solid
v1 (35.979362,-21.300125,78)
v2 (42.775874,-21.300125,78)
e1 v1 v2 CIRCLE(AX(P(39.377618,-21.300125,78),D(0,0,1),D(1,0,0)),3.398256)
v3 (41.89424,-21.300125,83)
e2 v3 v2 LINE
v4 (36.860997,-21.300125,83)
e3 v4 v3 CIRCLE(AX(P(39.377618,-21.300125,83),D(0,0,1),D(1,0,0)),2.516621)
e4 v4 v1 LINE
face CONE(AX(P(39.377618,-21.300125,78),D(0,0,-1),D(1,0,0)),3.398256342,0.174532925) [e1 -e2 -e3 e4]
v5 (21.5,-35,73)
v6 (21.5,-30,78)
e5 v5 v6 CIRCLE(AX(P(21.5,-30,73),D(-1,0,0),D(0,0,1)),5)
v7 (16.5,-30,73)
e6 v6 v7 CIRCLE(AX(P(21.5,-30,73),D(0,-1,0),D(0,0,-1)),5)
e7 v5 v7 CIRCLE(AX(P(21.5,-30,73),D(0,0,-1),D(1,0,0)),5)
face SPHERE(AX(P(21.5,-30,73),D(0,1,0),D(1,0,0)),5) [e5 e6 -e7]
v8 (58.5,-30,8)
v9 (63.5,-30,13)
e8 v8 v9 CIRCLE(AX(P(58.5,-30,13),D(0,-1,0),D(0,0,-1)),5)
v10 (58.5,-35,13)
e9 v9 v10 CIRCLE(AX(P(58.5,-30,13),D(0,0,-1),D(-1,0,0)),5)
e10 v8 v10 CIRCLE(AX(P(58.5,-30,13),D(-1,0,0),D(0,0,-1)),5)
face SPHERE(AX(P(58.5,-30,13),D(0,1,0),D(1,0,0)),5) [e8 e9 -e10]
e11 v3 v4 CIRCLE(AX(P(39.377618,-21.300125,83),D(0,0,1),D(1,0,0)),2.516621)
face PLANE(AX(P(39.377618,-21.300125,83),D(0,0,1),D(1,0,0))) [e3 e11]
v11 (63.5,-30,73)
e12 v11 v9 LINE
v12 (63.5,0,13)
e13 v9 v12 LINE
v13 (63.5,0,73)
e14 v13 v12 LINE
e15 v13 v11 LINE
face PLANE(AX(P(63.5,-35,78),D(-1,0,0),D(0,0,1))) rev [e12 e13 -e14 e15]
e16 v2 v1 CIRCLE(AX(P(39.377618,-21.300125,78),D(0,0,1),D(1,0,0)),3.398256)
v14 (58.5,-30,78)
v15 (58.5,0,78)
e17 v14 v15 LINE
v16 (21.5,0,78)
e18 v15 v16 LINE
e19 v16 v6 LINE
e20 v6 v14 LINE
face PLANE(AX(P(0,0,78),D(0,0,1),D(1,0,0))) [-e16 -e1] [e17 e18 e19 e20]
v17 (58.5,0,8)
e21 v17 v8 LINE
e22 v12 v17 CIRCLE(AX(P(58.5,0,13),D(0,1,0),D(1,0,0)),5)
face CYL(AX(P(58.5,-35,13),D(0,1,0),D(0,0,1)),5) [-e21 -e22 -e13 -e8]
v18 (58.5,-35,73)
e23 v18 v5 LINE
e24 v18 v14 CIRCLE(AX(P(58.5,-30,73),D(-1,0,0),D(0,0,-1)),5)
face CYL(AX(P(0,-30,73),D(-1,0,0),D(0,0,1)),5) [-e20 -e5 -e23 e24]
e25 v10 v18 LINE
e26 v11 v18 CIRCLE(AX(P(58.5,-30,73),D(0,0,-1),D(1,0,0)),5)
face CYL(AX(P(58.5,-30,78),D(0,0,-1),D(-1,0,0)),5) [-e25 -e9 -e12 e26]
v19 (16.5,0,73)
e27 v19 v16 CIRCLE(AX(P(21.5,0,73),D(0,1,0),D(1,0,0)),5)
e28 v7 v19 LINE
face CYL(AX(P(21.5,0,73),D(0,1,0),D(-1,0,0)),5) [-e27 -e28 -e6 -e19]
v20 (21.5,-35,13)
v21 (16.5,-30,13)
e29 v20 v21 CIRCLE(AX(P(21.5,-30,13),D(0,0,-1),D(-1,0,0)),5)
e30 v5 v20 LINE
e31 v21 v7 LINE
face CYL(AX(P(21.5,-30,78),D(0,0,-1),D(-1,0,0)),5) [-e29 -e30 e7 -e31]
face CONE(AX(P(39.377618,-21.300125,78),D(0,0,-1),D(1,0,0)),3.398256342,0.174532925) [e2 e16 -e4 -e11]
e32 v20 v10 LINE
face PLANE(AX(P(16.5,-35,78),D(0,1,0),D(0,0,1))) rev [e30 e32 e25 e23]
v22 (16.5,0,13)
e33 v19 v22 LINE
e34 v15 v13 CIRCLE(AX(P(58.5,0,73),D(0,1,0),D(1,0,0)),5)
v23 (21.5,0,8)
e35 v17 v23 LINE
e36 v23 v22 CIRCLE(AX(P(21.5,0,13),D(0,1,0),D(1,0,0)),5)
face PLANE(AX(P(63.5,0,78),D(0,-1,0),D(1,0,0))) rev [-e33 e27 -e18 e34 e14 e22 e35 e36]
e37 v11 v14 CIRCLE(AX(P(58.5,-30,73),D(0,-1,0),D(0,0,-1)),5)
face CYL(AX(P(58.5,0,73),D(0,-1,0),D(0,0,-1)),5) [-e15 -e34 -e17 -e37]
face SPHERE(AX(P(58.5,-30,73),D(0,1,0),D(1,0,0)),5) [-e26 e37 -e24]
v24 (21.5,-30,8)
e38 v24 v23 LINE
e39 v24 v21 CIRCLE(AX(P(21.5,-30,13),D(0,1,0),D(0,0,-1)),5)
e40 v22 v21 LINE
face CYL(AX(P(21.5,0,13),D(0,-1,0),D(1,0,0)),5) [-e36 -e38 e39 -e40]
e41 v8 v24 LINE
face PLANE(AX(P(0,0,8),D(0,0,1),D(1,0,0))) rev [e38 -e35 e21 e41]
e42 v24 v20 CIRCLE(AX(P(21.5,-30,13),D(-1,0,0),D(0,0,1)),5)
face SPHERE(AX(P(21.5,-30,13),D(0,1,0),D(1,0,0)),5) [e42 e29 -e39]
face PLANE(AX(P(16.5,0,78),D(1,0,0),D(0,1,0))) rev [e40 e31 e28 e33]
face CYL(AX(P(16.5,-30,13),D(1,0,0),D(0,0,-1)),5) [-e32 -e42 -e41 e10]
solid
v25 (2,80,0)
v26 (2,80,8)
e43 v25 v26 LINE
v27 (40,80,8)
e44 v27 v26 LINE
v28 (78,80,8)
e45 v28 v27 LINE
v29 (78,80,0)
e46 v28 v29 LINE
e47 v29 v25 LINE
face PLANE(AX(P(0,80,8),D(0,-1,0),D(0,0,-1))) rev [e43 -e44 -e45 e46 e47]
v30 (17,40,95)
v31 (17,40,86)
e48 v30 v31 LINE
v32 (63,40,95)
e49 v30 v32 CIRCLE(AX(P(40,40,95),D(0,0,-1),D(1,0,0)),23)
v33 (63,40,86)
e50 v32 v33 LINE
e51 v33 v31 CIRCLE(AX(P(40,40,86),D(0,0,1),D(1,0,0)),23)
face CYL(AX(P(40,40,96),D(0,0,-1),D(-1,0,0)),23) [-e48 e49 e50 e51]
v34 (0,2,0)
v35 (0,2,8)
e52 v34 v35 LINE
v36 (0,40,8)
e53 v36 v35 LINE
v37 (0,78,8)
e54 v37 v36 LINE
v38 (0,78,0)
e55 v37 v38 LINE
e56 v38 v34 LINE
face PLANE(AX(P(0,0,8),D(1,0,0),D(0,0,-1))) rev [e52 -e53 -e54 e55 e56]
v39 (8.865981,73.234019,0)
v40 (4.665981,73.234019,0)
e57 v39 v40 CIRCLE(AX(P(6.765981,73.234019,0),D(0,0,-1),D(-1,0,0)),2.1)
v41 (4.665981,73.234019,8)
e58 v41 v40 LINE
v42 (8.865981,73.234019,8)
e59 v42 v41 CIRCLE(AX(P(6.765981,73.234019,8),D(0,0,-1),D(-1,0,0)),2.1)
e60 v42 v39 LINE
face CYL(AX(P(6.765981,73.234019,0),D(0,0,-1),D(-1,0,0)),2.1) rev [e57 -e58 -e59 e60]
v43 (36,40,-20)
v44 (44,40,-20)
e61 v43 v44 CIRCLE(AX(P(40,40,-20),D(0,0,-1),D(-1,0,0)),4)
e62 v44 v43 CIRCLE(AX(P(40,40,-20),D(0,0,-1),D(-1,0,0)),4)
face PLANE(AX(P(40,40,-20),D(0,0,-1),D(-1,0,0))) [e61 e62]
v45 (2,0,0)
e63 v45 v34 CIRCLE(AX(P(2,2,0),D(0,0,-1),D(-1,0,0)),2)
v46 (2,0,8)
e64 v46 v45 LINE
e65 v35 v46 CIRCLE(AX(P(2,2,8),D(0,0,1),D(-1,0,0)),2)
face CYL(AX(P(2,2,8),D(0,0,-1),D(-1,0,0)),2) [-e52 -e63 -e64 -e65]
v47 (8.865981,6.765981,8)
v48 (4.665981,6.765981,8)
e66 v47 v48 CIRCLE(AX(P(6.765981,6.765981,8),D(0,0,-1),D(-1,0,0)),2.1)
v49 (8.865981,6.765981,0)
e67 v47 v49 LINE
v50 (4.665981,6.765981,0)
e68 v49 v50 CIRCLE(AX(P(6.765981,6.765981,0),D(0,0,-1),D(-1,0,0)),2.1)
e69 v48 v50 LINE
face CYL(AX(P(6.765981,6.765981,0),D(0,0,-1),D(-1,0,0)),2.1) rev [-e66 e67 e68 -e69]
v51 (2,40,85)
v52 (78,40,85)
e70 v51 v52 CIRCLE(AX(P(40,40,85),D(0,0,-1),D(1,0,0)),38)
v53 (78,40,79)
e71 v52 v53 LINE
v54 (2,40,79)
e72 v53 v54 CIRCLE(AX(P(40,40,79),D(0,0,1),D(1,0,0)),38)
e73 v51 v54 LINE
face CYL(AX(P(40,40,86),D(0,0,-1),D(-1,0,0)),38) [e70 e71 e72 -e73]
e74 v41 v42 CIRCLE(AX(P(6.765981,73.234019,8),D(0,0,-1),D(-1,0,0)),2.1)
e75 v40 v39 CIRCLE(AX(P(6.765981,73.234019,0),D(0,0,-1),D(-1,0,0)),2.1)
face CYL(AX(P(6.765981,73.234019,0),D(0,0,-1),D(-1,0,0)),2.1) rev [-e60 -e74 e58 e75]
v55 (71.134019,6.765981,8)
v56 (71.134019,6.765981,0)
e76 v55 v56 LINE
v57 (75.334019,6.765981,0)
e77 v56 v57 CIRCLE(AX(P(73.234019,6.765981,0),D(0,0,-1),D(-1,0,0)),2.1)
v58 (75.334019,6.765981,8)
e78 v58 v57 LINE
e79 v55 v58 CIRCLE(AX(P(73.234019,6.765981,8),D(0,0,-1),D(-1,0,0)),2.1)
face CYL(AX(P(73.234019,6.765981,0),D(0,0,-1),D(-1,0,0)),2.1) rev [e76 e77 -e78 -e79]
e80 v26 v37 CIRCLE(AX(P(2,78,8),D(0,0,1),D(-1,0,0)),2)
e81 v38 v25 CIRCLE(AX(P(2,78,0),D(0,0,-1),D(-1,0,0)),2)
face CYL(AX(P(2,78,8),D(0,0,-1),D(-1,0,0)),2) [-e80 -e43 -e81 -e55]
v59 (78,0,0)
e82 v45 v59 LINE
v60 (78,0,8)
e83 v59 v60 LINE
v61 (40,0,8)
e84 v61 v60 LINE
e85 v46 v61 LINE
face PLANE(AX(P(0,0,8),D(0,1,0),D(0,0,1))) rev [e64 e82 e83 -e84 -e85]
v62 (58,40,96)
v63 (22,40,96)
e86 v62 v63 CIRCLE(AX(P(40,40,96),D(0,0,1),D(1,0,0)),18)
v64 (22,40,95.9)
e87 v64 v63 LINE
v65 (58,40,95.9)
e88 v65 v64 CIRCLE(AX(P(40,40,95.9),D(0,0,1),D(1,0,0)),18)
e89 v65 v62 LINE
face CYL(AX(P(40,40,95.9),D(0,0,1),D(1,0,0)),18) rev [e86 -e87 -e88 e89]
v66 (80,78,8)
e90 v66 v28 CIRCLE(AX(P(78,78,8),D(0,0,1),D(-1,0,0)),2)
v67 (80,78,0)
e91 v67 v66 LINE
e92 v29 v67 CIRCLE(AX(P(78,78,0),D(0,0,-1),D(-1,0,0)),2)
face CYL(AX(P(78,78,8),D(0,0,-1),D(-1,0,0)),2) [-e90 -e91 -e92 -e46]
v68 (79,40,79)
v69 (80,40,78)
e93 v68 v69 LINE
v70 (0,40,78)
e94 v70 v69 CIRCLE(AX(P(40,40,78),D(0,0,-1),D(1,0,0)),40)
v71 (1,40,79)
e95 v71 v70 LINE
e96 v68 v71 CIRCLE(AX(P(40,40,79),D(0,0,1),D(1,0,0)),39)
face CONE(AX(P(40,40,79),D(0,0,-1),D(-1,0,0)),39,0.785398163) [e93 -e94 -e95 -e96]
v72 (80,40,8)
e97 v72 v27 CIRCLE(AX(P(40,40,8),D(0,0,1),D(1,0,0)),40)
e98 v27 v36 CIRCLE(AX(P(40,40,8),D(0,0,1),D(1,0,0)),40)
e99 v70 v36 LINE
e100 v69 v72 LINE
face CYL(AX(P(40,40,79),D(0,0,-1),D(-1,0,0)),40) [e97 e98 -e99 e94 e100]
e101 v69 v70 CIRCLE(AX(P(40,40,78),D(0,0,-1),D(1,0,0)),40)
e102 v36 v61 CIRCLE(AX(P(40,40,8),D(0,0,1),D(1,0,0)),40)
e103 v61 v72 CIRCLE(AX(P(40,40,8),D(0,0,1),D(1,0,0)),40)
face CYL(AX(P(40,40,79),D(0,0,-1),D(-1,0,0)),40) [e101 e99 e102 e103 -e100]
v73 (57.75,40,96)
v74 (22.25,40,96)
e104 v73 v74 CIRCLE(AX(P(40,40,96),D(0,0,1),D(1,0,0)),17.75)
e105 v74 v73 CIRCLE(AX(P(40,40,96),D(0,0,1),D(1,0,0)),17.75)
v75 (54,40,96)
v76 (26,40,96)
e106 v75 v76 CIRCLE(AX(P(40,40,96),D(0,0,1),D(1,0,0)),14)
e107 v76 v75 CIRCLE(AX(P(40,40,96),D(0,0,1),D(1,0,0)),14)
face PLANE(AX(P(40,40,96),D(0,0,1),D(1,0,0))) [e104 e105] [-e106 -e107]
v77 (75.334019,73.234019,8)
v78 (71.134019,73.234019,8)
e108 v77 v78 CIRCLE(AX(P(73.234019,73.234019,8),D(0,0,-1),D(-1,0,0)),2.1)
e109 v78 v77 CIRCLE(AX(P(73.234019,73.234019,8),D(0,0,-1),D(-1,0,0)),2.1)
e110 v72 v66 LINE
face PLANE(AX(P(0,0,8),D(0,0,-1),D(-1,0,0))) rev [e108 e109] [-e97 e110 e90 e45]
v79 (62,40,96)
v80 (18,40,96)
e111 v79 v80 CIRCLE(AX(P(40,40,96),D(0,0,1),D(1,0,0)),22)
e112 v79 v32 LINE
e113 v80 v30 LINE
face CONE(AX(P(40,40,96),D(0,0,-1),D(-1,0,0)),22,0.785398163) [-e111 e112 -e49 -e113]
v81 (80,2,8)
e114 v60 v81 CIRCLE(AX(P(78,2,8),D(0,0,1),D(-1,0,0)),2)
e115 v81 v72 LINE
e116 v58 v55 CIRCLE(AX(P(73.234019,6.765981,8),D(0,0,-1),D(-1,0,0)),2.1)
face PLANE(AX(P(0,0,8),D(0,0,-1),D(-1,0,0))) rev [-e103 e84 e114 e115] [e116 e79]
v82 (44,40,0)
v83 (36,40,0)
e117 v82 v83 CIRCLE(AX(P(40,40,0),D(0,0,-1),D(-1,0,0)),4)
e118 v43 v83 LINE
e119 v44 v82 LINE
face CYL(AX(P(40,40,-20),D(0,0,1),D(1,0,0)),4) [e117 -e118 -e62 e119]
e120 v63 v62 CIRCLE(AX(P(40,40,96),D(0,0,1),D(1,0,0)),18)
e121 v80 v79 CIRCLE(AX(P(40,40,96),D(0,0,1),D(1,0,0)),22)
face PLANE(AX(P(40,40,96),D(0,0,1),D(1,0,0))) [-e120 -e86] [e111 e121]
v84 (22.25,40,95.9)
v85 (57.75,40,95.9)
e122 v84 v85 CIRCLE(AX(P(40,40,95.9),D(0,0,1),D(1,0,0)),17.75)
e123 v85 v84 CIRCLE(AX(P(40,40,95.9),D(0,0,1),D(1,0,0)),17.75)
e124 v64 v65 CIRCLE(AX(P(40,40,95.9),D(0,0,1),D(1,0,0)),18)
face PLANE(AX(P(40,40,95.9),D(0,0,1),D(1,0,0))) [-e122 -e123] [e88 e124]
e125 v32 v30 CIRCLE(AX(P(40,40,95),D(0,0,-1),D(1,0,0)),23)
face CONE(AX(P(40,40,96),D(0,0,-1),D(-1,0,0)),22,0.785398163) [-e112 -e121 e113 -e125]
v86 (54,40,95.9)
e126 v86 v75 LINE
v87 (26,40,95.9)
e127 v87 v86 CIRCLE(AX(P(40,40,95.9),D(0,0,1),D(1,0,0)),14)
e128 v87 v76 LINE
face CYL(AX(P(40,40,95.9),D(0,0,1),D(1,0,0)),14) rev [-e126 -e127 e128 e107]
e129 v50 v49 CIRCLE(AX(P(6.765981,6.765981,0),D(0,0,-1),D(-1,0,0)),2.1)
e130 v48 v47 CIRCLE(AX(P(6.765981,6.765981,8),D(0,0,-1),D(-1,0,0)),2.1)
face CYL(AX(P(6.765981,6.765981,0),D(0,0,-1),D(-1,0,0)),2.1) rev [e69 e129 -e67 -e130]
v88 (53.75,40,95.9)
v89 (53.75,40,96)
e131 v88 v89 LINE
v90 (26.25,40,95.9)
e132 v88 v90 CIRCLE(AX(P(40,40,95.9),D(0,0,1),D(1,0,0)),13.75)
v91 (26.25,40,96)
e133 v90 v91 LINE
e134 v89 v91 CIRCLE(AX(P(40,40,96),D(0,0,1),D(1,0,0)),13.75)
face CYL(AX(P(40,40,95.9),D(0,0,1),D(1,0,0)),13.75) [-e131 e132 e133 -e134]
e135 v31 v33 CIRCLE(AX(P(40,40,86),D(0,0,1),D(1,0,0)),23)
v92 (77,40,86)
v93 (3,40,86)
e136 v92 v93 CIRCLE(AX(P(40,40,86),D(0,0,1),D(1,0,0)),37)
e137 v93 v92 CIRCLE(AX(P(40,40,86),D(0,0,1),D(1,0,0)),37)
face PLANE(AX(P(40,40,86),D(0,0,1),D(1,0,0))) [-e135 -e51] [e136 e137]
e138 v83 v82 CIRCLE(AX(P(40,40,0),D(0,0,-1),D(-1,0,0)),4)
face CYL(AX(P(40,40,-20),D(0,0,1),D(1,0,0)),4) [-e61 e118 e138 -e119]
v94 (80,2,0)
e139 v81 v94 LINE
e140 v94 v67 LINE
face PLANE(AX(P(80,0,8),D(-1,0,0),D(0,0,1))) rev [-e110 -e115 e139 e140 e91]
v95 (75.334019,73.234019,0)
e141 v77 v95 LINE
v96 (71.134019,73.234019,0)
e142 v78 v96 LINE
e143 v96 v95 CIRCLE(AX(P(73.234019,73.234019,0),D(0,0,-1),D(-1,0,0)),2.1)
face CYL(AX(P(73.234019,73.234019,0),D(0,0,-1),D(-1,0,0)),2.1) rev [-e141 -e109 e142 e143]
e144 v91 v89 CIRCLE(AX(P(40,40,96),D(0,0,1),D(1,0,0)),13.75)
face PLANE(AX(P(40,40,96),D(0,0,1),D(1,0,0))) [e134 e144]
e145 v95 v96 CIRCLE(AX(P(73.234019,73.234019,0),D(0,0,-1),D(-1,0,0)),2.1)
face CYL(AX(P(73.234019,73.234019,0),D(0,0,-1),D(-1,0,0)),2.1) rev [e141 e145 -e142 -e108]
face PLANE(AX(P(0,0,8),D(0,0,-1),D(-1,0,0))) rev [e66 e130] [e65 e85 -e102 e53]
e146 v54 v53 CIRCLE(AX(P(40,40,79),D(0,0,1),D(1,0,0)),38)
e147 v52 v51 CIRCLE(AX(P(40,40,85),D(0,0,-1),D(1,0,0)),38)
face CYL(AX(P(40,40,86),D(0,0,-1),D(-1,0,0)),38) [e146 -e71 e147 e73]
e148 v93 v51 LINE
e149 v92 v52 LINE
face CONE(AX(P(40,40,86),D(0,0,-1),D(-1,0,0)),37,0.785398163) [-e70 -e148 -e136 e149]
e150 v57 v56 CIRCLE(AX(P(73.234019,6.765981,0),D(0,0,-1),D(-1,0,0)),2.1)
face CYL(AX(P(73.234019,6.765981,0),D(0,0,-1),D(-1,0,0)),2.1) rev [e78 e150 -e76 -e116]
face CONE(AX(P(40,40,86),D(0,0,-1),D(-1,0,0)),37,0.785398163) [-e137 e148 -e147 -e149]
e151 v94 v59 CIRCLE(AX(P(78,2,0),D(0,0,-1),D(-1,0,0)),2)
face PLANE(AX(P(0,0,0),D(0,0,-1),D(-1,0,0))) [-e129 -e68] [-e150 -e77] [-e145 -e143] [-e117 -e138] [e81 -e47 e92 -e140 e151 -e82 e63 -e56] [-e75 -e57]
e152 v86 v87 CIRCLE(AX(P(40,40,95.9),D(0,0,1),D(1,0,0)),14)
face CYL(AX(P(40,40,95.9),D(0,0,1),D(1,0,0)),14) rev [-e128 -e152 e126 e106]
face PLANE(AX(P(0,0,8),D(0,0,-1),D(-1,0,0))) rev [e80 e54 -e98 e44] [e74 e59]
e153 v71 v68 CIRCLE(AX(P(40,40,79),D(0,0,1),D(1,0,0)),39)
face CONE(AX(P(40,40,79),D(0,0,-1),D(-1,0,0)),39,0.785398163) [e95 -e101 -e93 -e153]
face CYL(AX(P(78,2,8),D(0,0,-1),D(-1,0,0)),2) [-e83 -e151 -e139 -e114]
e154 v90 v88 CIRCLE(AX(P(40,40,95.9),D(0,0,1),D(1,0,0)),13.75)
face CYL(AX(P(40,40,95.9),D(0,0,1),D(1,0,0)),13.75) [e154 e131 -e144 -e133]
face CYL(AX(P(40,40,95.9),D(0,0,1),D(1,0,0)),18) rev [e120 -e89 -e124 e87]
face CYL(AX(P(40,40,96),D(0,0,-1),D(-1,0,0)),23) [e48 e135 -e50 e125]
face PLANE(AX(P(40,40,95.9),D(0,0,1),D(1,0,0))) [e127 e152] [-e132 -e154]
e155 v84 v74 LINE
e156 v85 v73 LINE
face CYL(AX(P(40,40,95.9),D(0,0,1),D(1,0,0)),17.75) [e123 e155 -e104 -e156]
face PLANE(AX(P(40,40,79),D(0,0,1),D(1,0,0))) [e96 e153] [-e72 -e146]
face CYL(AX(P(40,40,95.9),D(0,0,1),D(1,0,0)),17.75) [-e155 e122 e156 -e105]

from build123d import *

# Parameters (mm, degrees)
SKETCH_1_W                  = 80
SKETCH_1_H                  = 80
EXTRUDE_1_DEPTH             = 8
SKETCH_2_R                  = 40
EXTRUDE_2_DEPTH             = 71
SKETCH_3_R                  = 38
EXTRUDE_3_DEPTH             = 7
SKETCH_4_R                  = 23
EXTRUDE_4_DEPTH             = 10
SKETCH_5_R                  = 4
EXTRUDE_5_DEPTH             = 20
FILLET_1_R                  = 2
CHAMFER_1_SIZE              = 1
SKETCH_6_R                  = 18
SKETCH_6_R_2                = 17.75
SKETCH_6_R_3                = 14
SKETCH_6_R_4                = 13.75
CUT_EXTRUDE_2_DEPTH         = 0.1
SKETCH_8_W                  = 47
SKETCH_8_H                  = 35
EXTRUDE_6_DEPTH             = 70
FILLET_2_R                  = 5
SKETCH_9_R                  = 3.398256342
EXTRUDE_7_DEPTH             = 5
EXTRUDE_7_TAPER             = 10
SKETCH_13_W                 = 2.1
SKETCH_13_H                 = 96
HOLE_WIZARD_M5_1_AT_2_COUNT = 2
HOLE_WIZARD_M5_1_AT_2_PITCH = 66.468037432
HOLE_WIZARD_M5_1_AT_3_COUNT = 2
HOLE_WIZARD_M5_1_AT_3_PITCH = 94
HOLE_WIZARD_M5_1_AT_4_COUNT = 2
HOLE_WIZARD_M5_1_AT_4_PITCH = 66.468037432


with BuildPart() as part:
    # 草图1 → 凸台-拉伸1 (new body)
    with BuildSketch(Plane.XY):
        with Locations((40, 40)):
            Rectangle(SKETCH_1_W, SKETCH_1_H)
    extrude(amount=EXTRUDE_1_DEPTH)

    # 草图2 → 凸台-拉伸2 (add)
    with BuildSketch(Plane.XY.offset(8)):
        with Locations((40, 40)):
            Circle(SKETCH_2_R)
    extrude(amount=EXTRUDE_2_DEPTH)

    # 草图3 → 凸台-拉伸3 (add)
    with BuildSketch(Plane.XY.offset(79)):
        with Locations((40, 40)):
            Circle(SKETCH_3_R)
    extrude(amount=EXTRUDE_3_DEPTH)

    # 草图4 → 凸台-拉伸4 (add)
    with BuildSketch(Plane.XY.offset(86)):
        with Locations((40, 40)):
            Circle(SKETCH_4_R)
    extrude(amount=EXTRUDE_4_DEPTH)

    # 草图5 → 凸台-拉伸5 (add)
    with BuildSketch(Plane(origin=(0, 0, 0), x_dir=(-1, 0, 0), z_dir=(0, 0, -1))):
        with Locations((-40, 40)):
            Circle(SKETCH_5_R)
    extrude(amount=EXTRUDE_5_DEPTH)

    # 圆角1
    fillet_1_edges = [part.edges().sort_by_distance(p)[0] for p in [
        (0, 80, 4),
        (80, 80, 4),
        (80, 0, 4),
        (0, 0, 4),
    ]]
    fillet(fillet_1_edges, radius=FILLET_1_R)

    # 倒角1
    chamfer_1_edges = [part.edges().sort_by_distance(p)[0] for p in [
        (0, 40, 79),
        (2, 40, 86),
        (17, 40, 96),
    ]]
    chamfer(chamfer_1_edges, length=CHAMFER_1_SIZE)

    # 草图6 → 切除-拉伸2 (cut)
    # profile 1 of 2: a face of its own
    with BuildSketch(Plane.XY.offset(96)):
        with Locations((40, 40)):
            Circle(SKETCH_6_R)
        with Locations((40, 40)):
            Circle(SKETCH_6_R_2, mode=Mode.SUBTRACT)
    # profile 2 of 2: a face of its own
    with BuildSketch(Plane.XY.offset(96)):
        with Locations((40, 40)):
            Circle(SKETCH_6_R_3)
        with Locations((40, 40)):
            Circle(SKETCH_6_R_4, mode=Mode.SUBTRACT)
    extrude(amount=-CUT_EXTRUDE_2_DEPTH, mode=Mode.SUBTRACT)

    # 草图13 → M5 螺纹孔1 (revolve, cut)
    with BuildSketch(Plane(origin=(73.234018716, 73.234018716, 0), x_dir=(0, 1, 0), z_dir=(1, 0, 0))):
        with Locations((1.05, 48)):
            Rectangle(SKETCH_13_W, SKETCH_13_H)
    hole_wizard_m5_1 = revolve(axis=Axis((73.234018716, 73.234018716, -6.35), (0, 0, 1)), mode=Mode.SUBTRACT)

    # M5 螺纹孔1 at 2: M5 螺纹孔1 ×2
    with Locations(*[(-i * HOLE_WIZARD_M5_1_AT_2_PITCH, 0, 0) for i in range(1, HOLE_WIZARD_M5_1_AT_2_COUNT)]):
        add(hole_wizard_m5_1, mode=Mode.SUBTRACT)

    # M5 螺纹孔1 at 3: M5 螺纹孔1 ×2
    with Locations(*[Vector(-0.7071067811865476, -0.7071067811865476, 0) * (i * HOLE_WIZARD_M5_1_AT_3_PITCH) for i in range(1, HOLE_WIZARD_M5_1_AT_3_COUNT)]):
        add(hole_wizard_m5_1, mode=Mode.SUBTRACT)

    # M5 螺纹孔1 at 4: M5 螺纹孔1 ×2
    with Locations(*[(0, -i * HOLE_WIZARD_M5_1_AT_4_PITCH, 0) for i in range(1, HOLE_WIZARD_M5_1_AT_4_COUNT)]):
        add(hole_wizard_m5_1, mode=Mode.SUBTRACT)


with BuildPart() as body_2:
    # 草图8 → 凸台-拉伸6 (new body)
    with BuildSketch(Plane.XY.offset(8)):
        with Locations((40, -17.5)):
            Rectangle(SKETCH_8_W, SKETCH_8_H)
    extrude(amount=EXTRUDE_6_DEPTH)

    # 圆角2
    fillet_2_edges = [body_2.edges().sort_by_distance(p)[0] for p in [
        (16.5, -17.5, 78),
        (40, -35, 78),
        (63.5, -17.5, 78),
        (40, -35, 8),
        (16.5, -17.5, 8),
        (63.5, -17.5, 8),
        (63.5, -35, 43),
        (16.5, -35, 43),
    ]]
    fillet(fillet_2_edges, radius=FILLET_2_R)

    # 草图9 → 凸台-拉伸7 (add)
    with BuildSketch(Plane.XY.offset(78)):
        with Locations((39.377618123, -21.300124573)):
            Circle(SKETCH_9_R)
    extrude(amount=EXTRUDE_7_DEPTH, taper=EXTRUDE_7_TAPER)


solid = Compound([part.part, body_2.part])
